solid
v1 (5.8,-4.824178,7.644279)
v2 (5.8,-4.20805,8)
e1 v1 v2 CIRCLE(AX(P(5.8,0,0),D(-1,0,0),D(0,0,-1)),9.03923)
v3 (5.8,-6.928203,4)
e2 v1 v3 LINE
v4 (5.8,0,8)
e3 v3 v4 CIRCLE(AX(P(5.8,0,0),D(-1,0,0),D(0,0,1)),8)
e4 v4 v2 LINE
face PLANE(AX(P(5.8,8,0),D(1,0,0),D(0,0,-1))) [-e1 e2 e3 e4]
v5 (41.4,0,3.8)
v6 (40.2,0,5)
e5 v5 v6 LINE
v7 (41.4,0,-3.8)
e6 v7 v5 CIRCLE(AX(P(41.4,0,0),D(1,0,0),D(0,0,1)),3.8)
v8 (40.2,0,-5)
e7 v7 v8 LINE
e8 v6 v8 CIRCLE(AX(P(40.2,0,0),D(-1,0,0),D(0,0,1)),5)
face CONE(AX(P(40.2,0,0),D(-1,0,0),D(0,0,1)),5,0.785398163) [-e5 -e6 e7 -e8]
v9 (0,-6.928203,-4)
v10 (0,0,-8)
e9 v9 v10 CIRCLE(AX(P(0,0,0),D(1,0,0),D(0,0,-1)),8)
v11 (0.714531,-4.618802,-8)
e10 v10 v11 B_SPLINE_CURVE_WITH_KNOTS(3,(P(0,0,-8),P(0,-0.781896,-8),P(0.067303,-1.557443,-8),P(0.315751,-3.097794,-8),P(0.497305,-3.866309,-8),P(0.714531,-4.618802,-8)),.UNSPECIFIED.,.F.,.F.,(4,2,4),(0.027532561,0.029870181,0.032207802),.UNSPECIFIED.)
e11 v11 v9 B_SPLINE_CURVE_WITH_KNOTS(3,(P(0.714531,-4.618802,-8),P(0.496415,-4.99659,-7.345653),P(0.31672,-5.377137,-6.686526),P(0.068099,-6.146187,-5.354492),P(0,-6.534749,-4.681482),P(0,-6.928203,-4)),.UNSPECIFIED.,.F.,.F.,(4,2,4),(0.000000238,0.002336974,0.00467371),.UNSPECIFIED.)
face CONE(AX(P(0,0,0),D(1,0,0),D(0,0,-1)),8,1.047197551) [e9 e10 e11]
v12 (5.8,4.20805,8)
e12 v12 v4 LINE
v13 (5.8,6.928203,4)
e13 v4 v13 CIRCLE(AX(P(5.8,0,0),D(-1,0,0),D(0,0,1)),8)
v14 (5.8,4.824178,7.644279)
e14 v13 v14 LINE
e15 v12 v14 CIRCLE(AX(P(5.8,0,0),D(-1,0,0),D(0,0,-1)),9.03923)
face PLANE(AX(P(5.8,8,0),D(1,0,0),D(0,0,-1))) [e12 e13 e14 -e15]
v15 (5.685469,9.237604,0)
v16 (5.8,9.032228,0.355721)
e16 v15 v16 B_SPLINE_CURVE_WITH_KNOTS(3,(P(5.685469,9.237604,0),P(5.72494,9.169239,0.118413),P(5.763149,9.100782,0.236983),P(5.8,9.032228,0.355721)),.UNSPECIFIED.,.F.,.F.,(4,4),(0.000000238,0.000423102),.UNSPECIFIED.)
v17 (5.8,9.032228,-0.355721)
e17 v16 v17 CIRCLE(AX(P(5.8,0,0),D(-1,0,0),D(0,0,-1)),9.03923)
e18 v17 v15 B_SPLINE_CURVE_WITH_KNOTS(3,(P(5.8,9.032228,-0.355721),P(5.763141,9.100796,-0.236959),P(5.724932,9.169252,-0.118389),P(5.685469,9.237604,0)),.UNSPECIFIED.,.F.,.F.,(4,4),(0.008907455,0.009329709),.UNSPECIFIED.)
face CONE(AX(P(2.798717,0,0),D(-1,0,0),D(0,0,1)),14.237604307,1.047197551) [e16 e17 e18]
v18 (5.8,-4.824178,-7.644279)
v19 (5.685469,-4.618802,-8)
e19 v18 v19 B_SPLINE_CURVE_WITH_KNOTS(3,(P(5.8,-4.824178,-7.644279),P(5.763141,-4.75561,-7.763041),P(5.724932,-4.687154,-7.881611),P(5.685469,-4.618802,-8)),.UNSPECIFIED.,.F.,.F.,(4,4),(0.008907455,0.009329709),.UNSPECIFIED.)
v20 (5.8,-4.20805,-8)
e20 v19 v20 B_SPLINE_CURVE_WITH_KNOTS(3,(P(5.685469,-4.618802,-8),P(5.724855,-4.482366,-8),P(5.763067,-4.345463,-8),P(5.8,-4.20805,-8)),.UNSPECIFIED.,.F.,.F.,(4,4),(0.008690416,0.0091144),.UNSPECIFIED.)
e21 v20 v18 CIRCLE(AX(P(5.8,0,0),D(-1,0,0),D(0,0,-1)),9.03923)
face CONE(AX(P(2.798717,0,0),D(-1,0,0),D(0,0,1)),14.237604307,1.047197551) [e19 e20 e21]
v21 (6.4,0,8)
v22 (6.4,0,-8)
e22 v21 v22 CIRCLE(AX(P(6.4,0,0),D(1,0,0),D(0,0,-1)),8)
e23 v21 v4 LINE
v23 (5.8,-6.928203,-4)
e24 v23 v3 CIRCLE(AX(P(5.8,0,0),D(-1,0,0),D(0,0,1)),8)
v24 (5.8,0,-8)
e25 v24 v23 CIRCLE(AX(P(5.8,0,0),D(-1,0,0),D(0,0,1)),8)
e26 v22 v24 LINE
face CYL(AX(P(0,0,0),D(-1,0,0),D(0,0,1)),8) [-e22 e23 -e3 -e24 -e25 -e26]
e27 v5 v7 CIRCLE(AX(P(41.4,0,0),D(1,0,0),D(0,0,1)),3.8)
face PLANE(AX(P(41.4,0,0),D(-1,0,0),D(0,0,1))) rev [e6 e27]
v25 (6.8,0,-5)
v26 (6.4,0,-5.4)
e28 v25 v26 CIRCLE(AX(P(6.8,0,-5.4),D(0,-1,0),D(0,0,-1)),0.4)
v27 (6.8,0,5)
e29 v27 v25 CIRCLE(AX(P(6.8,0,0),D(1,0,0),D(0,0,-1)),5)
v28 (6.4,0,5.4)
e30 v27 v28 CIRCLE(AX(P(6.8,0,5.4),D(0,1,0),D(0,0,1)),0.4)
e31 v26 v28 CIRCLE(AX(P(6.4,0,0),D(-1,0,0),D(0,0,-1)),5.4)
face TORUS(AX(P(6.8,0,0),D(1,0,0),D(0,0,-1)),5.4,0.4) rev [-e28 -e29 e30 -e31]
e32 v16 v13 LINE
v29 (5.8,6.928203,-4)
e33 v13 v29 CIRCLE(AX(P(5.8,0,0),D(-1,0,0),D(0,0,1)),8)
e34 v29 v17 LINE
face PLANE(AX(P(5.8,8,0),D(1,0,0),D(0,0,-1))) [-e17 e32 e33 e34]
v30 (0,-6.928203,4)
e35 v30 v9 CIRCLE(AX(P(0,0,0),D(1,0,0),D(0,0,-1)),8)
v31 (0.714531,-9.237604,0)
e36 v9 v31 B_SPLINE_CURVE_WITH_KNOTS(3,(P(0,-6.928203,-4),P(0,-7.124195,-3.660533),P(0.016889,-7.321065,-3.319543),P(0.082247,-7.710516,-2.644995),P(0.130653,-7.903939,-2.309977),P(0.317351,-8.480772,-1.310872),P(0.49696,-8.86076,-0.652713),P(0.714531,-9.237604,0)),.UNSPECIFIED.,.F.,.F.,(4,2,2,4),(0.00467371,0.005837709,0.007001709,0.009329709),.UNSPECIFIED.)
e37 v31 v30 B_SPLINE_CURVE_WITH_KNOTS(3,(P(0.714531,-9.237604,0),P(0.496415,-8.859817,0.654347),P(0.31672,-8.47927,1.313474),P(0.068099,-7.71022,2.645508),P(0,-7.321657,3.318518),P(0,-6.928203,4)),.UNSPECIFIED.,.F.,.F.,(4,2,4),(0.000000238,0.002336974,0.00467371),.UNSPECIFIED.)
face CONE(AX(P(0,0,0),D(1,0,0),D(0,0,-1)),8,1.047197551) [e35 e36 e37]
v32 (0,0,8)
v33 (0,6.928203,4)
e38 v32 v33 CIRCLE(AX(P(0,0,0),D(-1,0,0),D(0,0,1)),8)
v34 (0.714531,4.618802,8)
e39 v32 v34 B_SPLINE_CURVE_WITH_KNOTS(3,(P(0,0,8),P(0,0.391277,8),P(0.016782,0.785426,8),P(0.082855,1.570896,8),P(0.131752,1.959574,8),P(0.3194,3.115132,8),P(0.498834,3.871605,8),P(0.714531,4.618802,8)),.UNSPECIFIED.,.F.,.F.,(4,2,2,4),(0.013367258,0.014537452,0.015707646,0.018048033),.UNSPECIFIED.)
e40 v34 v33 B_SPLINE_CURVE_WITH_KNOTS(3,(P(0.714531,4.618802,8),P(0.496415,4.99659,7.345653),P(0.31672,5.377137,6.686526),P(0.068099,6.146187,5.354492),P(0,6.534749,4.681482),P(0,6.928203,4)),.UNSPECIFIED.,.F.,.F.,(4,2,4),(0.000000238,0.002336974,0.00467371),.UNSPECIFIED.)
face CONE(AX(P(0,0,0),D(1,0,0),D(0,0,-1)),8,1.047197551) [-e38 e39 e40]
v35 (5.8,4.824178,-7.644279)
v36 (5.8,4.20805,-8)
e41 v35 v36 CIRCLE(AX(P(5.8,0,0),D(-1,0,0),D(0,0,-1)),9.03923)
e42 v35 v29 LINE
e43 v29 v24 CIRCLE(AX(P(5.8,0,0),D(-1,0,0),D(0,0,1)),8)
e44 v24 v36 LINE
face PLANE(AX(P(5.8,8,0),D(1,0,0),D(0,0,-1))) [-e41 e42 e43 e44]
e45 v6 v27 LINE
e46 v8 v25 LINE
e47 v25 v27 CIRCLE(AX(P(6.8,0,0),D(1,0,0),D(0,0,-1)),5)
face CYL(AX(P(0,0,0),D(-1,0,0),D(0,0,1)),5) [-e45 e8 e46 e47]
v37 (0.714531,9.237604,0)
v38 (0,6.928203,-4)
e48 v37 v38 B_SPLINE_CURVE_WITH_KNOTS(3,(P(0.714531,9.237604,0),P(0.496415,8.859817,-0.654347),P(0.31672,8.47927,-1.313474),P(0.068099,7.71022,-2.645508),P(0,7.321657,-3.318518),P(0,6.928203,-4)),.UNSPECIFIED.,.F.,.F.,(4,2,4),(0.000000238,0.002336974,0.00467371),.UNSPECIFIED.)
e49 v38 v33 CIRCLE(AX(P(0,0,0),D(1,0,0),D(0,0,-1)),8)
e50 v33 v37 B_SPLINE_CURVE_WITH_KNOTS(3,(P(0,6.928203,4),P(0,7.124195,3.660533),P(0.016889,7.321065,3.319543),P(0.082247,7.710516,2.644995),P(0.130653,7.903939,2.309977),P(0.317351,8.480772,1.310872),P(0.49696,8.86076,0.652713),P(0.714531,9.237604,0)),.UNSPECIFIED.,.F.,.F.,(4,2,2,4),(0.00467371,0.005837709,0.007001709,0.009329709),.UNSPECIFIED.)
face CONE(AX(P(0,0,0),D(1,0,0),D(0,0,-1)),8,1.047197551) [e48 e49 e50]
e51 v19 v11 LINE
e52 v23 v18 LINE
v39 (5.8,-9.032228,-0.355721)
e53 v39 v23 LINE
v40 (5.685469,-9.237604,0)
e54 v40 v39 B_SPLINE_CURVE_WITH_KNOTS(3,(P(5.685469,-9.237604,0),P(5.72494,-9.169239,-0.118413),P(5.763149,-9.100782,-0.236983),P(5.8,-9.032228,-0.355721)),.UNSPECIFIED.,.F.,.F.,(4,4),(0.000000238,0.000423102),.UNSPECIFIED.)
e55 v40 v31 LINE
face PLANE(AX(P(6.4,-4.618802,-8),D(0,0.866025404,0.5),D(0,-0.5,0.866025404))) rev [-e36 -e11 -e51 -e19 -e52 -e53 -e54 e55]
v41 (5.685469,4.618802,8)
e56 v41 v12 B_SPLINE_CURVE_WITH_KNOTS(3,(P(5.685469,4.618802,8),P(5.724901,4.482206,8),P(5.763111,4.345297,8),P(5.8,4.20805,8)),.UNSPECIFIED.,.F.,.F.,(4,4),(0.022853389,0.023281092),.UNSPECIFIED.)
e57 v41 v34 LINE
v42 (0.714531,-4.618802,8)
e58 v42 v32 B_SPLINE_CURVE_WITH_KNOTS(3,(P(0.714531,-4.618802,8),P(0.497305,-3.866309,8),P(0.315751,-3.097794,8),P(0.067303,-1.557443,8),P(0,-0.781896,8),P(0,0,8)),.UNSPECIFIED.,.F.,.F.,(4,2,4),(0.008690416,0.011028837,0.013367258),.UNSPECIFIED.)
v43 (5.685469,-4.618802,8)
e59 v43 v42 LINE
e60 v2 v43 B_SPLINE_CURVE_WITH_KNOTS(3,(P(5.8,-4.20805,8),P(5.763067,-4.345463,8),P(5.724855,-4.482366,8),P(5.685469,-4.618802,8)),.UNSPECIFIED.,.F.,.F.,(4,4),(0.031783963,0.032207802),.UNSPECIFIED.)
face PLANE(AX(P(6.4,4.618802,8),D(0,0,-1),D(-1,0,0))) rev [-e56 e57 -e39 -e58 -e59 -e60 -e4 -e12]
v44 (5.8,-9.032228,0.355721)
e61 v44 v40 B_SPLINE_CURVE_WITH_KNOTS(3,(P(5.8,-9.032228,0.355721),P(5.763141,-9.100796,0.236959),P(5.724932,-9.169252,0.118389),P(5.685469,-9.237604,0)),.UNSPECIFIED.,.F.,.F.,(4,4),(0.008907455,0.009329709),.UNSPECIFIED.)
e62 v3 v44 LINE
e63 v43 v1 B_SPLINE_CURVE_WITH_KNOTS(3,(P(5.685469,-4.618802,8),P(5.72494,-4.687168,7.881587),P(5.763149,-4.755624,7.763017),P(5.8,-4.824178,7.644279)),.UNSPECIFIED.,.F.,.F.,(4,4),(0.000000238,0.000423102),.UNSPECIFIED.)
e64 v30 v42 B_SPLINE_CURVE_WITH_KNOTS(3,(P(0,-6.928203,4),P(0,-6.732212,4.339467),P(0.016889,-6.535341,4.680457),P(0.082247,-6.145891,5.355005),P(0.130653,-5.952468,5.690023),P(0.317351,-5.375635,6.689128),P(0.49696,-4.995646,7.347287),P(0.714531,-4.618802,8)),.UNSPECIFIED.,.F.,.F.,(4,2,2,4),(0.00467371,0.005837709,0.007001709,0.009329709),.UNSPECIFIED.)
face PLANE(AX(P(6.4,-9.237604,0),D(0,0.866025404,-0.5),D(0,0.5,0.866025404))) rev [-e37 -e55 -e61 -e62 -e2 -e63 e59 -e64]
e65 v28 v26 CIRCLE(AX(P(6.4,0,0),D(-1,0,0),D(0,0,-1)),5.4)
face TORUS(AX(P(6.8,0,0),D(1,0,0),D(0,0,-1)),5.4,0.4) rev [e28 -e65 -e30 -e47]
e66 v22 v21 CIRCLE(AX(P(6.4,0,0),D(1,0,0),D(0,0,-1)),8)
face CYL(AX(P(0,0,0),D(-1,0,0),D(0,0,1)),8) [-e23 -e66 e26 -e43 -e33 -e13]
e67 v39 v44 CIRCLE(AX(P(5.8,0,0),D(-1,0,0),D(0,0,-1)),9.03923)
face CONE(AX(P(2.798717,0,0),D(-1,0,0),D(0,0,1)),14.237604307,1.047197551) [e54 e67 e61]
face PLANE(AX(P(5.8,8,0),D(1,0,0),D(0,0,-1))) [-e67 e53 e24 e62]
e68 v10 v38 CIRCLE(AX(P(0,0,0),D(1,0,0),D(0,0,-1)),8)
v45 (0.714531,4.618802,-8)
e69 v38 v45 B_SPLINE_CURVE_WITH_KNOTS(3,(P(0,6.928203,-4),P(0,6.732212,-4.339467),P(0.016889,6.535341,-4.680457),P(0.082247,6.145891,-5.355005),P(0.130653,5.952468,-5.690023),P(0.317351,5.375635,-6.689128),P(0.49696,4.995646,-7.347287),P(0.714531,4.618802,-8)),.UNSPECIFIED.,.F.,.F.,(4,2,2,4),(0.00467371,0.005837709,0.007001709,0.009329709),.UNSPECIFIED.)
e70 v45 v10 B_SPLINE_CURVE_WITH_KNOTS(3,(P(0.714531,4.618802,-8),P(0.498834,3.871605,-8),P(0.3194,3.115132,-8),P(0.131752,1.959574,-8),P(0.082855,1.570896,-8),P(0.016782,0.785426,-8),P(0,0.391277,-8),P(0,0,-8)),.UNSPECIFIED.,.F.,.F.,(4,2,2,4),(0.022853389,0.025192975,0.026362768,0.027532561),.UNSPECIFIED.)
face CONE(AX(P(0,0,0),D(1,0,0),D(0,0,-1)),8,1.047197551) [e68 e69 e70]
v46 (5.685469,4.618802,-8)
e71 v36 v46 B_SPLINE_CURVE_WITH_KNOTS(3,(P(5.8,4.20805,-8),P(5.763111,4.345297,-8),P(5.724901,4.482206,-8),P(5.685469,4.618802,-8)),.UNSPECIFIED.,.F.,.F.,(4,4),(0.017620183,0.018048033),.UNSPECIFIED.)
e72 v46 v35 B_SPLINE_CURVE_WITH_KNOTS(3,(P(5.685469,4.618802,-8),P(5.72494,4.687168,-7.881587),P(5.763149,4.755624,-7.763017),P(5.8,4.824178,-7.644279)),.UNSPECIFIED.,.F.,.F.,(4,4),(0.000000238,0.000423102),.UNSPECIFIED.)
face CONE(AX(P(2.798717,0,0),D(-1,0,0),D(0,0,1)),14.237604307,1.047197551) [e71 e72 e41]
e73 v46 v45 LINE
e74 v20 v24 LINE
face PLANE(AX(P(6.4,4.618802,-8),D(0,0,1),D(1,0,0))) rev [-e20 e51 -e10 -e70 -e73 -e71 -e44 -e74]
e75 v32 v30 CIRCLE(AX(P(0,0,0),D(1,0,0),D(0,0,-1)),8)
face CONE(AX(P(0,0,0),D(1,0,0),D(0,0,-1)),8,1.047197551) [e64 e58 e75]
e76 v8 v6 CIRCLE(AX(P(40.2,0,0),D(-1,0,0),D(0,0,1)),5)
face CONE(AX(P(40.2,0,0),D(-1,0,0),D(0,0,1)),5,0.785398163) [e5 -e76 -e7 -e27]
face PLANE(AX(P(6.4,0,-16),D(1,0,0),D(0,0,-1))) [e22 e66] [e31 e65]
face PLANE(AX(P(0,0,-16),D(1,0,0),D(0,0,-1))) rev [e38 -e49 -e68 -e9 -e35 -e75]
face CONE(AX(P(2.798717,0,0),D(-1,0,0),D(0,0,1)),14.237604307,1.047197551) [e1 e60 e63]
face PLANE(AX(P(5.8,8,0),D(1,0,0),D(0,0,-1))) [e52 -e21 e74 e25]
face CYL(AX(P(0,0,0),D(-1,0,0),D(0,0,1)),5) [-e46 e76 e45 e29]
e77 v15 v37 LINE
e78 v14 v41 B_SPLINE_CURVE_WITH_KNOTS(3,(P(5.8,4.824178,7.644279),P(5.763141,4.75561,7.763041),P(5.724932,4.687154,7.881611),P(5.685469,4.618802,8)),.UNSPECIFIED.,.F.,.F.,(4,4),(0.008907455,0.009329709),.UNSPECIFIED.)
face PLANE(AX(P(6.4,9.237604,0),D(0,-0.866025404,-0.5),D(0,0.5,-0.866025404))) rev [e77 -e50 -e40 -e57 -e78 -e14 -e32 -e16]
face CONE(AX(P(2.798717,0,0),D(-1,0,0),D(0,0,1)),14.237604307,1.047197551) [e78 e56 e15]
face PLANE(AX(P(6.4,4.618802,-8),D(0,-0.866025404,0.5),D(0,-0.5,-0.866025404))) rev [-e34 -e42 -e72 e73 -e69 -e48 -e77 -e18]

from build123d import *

# Parameters (mm, degrees)
EXTRUDE_368_DEPTH = 6.4
SKETCH_4_W        = 0.6
SKETCH_4_H        = 11.237604307
CHAMFER_1891_SIZE = 1.2
FILLET_1936_R     = 0.4


with BuildPart() as part:
    # 草图1 → Extrude 368 (new body)
    with BuildSketch(Plane(origin=(0, 0, 0), x_dir=(0, 0, -1), z_dir=(1, 0, 0))):
        Polygon((8, 4.618802154), (8, -4.618802154), (0, -9.237604307), (-8, -4.618802154), (-8, 4.618802154), (0, 9.237604307), align=None)
    extrude(amount=EXTRUDE_368_DEPTH)

    # 草图2 → 凸台-旋转1 (revolve)
    with BuildSketch(Plane.XY, mode=Mode.PRIVATE) as revolve_1_sk:
        Polygon((0, 0), (41.4, 0), (41.4, 3.701), (41.4, 5), (0, 5), align=None)
    revolve(revolve_1_sk.sketch.rotate(Axis((0, 0, 0), (1, 0, 0)), 90), axis=Axis((0, 0, 0), (1, 0, 0)))

    # 草图3 → 切除-旋转1 (revolve, cut)
    with BuildSketch(Plane.XY):
        Polygon((0, 8), (3.601282526, 14.237604307), (3.601282526, 19.237604307), (-10, 19.237604307), (-10, 8), align=None)
    revolve(axis=Axis((0, 0, 0), (1, 0, 0)), mode=Mode.SUBTRACT)

    # 草图5 → 切除-旋转2 (revolve, cut)
    with BuildSketch(Plane.XY):
        Polygon((6.4, 8), (2.798717474, 14.237604307), (2.798717474, 19.237604307), (12.798717474, 19.237604307), (12.798717474, 8), align=None)
    revolve(axis=Axis((0, 0, 0), (1, 0, 0)), mode=Mode.SUBTRACT)

    # 草图4 → 切除-旋转3 (revolve, cut)
    with BuildSketch(Plane.XY, mode=Mode.PRIVATE) as cut_revolve_3_sk:
        with Locations((6.1, 13.618802154)):
            Rectangle(SKETCH_4_W, SKETCH_4_H)
    revolve(cut_revolve_3_sk.sketch.rotate(Axis((0, 0, 0), (1, 0, 0)), 270), axis=Axis((0, 0, 0), (1, 0, 0)), mode=Mode.SUBTRACT)

    # Chamfer 1891
    chamfer_1891_edges = [part.edges().sort_by_distance(p)[0] for p in [
        (41.4, 0, -5),
    ]]
    chamfer(chamfer_1891_edges, length=CHAMFER_1891_SIZE)

    # Fillet 1936
    fillet_1936_edges = [part.edges().sort_by_distance(p)[0] for p in [
        (6.4, 0, -5),
    ]]
    fillet(fillet_1936_edges, radius=FILLET_1936_R)


solid = part.part
